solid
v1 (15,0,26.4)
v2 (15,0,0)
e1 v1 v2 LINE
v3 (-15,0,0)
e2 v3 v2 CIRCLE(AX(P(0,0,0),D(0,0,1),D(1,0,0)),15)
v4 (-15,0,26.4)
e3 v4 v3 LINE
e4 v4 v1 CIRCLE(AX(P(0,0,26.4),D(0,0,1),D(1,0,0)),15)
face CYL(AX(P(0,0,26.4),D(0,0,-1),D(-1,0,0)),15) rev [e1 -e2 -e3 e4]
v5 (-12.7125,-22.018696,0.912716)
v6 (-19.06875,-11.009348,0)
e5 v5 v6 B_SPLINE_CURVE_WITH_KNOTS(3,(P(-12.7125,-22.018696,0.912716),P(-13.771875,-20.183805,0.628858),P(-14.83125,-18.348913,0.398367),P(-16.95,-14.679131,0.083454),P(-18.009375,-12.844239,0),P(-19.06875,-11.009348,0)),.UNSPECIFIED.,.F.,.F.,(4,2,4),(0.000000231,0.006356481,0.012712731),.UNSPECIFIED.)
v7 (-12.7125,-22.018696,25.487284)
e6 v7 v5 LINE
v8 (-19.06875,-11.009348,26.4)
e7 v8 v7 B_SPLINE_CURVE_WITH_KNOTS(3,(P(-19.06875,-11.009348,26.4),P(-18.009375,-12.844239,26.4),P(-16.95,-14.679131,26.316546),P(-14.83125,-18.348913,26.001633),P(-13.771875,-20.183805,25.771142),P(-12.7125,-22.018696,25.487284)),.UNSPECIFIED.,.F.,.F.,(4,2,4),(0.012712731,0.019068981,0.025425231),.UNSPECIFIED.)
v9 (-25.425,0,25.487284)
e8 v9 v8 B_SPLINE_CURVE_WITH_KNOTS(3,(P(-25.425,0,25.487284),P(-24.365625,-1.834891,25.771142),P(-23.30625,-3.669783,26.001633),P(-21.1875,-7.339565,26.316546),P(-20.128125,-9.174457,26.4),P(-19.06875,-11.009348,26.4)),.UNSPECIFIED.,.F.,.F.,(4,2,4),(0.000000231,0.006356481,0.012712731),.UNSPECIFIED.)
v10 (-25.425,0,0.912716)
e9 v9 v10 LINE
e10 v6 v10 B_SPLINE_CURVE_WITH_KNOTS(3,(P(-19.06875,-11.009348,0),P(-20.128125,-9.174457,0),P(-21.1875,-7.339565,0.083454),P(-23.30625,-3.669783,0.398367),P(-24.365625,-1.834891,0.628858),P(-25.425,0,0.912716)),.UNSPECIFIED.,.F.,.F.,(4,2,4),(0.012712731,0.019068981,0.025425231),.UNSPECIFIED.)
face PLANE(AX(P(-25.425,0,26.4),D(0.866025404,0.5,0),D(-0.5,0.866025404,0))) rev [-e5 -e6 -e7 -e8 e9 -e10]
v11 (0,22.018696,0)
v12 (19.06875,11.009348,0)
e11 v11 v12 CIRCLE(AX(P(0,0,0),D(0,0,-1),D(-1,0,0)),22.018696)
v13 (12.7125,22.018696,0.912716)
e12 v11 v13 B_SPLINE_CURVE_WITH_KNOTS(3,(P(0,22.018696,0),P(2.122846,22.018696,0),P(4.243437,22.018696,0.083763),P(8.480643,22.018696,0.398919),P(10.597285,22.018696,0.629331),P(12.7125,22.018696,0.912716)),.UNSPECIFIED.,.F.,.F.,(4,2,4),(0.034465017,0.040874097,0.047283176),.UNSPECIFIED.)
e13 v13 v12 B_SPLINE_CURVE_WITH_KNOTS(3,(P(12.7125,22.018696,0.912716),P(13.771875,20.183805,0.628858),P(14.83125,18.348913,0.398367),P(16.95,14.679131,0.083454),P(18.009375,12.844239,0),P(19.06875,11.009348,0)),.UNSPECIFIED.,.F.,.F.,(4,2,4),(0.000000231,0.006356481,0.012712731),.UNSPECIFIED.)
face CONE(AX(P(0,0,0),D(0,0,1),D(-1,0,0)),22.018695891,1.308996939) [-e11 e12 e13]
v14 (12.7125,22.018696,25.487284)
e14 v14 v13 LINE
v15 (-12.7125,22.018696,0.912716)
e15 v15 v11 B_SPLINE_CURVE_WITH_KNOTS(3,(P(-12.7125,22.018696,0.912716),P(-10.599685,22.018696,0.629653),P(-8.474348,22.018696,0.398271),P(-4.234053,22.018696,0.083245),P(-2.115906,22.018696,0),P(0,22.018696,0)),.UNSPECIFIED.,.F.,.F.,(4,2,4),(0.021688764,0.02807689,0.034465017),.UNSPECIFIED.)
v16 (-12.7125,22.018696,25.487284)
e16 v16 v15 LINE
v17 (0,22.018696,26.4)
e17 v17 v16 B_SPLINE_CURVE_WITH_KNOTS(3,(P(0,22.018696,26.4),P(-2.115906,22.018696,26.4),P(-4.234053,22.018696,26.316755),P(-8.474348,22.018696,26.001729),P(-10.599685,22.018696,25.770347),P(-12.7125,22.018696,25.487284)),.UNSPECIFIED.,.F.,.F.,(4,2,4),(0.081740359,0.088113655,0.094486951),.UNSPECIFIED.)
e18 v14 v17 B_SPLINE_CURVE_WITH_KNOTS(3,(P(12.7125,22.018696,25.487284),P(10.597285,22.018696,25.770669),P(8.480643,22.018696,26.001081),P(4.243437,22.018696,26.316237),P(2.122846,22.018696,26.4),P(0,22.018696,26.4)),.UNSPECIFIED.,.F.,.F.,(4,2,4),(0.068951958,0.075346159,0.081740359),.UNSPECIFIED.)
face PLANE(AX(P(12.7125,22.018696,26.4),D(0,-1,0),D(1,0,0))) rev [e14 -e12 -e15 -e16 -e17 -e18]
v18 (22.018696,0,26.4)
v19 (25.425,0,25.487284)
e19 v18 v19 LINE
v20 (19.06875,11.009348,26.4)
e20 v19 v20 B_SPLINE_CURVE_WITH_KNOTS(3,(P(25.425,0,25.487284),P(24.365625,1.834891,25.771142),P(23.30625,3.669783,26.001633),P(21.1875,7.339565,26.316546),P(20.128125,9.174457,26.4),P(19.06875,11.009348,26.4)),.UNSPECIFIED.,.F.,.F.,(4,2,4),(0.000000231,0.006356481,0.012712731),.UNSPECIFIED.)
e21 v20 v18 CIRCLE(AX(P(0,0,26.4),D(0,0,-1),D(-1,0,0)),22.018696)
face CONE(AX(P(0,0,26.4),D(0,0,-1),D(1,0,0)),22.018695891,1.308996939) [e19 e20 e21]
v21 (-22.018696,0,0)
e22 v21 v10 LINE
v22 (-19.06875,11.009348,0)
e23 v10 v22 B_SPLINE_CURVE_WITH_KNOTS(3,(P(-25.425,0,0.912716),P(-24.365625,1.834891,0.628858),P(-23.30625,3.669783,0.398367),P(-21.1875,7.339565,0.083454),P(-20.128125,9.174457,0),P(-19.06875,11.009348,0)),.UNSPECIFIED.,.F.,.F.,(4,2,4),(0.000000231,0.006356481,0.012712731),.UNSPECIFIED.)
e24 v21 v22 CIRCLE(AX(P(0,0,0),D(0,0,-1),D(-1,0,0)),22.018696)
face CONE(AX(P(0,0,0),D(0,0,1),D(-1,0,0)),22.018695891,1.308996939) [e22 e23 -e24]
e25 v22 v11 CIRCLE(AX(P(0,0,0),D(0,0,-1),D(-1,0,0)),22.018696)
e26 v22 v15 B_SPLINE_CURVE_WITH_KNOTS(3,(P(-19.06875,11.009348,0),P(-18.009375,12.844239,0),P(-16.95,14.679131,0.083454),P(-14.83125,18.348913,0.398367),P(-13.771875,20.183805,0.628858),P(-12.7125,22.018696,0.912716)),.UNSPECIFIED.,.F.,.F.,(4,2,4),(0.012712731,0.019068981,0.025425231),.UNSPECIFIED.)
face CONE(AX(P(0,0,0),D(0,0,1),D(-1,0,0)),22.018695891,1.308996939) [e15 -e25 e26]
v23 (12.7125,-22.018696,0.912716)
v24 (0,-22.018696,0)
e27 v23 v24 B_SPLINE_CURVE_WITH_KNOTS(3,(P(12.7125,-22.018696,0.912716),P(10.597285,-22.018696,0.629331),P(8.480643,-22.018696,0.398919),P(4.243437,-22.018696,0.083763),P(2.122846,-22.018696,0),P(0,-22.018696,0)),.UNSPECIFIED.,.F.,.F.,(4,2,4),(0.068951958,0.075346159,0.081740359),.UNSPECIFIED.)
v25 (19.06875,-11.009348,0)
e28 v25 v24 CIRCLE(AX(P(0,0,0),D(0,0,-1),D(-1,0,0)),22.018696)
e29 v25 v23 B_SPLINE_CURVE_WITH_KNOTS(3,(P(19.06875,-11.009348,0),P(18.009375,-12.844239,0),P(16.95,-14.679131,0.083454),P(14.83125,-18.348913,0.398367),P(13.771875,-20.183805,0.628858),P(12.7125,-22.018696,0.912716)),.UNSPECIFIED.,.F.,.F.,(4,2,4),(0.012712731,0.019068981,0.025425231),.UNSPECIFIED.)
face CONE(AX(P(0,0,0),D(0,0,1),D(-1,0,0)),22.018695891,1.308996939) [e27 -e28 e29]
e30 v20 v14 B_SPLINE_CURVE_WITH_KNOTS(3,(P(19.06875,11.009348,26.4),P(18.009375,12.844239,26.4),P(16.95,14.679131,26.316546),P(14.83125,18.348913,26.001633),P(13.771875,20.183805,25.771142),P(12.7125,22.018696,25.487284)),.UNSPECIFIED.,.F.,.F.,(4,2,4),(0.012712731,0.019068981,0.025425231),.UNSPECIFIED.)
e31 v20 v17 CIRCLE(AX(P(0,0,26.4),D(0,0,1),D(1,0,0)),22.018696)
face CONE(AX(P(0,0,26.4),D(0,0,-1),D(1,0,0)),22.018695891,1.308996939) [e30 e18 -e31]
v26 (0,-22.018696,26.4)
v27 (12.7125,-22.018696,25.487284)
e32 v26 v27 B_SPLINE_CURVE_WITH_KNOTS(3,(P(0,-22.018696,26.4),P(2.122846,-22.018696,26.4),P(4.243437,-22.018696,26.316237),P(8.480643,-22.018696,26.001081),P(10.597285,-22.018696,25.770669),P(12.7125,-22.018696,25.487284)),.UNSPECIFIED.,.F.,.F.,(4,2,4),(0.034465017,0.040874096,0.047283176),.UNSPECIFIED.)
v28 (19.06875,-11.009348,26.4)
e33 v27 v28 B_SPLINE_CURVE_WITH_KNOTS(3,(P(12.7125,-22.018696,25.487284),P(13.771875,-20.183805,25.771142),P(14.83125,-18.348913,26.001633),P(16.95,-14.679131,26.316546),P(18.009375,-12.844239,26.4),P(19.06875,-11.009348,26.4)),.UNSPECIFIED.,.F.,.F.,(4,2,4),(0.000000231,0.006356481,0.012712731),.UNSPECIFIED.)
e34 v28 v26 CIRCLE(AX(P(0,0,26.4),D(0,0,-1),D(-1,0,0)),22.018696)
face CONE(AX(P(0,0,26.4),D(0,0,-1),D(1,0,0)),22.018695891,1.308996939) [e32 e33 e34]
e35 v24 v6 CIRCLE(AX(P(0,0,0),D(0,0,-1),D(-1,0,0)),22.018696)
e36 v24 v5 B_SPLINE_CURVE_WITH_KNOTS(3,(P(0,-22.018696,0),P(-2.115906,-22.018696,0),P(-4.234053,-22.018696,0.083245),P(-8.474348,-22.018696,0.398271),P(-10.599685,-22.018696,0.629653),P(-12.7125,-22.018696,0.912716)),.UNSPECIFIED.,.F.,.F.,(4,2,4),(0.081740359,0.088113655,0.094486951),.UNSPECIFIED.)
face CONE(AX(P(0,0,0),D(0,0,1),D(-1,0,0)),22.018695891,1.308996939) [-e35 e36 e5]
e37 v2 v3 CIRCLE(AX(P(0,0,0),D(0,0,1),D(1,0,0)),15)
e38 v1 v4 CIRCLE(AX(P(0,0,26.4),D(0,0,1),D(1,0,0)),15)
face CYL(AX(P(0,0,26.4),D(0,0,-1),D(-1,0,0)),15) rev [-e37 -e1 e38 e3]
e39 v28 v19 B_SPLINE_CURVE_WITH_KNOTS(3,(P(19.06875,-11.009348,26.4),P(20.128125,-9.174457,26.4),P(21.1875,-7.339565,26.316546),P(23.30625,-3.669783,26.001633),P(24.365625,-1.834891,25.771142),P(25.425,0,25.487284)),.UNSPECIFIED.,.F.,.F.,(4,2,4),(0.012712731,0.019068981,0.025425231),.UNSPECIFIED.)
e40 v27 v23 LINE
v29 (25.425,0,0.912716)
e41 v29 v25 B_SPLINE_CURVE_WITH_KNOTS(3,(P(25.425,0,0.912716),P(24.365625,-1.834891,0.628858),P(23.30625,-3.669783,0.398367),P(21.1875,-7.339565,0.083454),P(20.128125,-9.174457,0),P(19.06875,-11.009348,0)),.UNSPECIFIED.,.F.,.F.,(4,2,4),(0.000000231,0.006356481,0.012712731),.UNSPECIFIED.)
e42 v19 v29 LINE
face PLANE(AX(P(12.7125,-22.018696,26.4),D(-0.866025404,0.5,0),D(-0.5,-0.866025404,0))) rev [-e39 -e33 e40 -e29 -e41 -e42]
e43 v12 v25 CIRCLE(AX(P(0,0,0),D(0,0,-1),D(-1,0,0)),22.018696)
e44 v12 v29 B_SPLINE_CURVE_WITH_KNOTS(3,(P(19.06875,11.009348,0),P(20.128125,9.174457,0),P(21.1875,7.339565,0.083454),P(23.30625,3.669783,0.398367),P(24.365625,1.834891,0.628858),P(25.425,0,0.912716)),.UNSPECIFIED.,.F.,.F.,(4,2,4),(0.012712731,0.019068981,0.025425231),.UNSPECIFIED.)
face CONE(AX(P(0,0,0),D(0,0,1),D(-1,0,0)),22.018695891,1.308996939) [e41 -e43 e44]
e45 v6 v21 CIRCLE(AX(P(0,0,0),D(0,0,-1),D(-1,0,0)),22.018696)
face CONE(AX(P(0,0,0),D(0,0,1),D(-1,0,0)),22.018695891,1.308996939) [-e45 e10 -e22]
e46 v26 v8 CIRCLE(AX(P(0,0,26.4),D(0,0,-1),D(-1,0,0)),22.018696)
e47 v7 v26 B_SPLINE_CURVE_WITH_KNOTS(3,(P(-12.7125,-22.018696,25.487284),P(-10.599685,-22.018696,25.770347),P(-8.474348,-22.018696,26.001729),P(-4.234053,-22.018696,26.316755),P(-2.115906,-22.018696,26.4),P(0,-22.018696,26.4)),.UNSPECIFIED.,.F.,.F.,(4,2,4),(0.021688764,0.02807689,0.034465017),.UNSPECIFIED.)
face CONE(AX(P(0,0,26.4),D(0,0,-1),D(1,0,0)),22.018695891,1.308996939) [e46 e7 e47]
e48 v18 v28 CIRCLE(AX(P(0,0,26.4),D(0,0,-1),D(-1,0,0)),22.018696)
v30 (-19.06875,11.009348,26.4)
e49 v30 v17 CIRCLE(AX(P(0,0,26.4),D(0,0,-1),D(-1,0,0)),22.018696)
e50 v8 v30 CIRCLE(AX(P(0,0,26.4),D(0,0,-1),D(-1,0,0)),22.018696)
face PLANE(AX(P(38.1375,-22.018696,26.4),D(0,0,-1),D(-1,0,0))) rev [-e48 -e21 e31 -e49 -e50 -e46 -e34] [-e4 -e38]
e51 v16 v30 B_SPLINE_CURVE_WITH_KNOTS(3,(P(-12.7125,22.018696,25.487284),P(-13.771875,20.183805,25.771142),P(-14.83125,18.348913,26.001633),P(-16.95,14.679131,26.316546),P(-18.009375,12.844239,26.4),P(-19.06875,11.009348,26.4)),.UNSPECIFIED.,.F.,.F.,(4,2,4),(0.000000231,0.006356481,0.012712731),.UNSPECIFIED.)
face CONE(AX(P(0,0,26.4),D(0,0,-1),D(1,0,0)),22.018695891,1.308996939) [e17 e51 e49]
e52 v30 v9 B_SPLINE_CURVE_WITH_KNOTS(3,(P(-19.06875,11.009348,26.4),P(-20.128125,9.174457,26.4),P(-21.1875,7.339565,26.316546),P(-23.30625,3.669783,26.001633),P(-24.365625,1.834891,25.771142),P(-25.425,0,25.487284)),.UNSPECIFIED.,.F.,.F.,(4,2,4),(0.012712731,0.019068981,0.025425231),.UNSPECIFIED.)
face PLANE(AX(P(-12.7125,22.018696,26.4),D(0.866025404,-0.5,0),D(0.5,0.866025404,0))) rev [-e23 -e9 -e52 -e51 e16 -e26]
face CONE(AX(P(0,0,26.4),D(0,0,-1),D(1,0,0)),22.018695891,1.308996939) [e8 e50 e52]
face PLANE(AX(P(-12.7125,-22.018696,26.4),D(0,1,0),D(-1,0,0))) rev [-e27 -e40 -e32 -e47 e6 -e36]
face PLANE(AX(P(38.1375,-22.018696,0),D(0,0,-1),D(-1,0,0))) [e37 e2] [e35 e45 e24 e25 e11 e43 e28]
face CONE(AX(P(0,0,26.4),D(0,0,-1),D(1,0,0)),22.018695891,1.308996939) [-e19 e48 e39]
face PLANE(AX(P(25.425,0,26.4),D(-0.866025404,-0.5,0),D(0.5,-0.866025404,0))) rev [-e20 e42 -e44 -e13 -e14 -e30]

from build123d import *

# Parameters (mm, degrees)
SKETCH_1_R          = 15
EXTRUDE_519_DEPTH   = 26.4
SKETCH_2_OUTSIDE_W  = 350.938
SKETCH_2_OUTSIDE_H  = 344.126
SKETCH_2_OUTSIDE_R  = 22.018695891
CUT_EXTRUDE_1_DEPTH = 38
CUT_EXTRUDE_1_DRAFT = -75
SKETCH_3_OUTSIDE_W  = 350.938
SKETCH_3_OUTSIDE_H  = 344.126
SKETCH_3_OUTSIDE_R  = 22.018695891
CUT_EXTRUDE_2_DEPTH = 38
CUT_EXTRUDE_2_DRAFT = -75


with BuildPart() as part:
    # 草图1 → Extrude 519 (new body)
    with BuildSketch(Plane.XY):
        Polygon((12.7125, 22.018695891), (-12.7125, 22.018695891), (-25.425, 0), (-12.7125, -22.018695891), (12.7125, -22.018695891), (25.425, 0), align=None)
        Circle(SKETCH_1_R, mode=Mode.SUBTRACT)
    extrude(amount=EXTRUDE_519_DEPTH)


with BuildPart() as cut_extrude_1_tool:
    # 草图2 outside → 切除-拉伸1 (with draft: the straight prism first)
    with BuildSketch(Plane(origin=(0, 0, 0), x_dir=(-1, 0, 0), z_dir=(0, 0, -1))):
        Rectangle(SKETCH_2_OUTSIDE_W, SKETCH_2_OUTSIDE_H)
        Circle(SKETCH_2_OUTSIDE_R, mode=Mode.SUBTRACT)
    extrude(amount=-CUT_EXTRUDE_1_DEPTH)
    # 切除-拉伸1: the draft: its side faces are tilted about the plane it starts from
    cut_extrude_1_sides = [cut_extrude_1_tool.faces().sort_by_distance(p)[0] for p in [
        (0, -172.063, 19),
        (-175.469, 0, 19),
        (0, 172.063, 19),
        (175.469, 0, 19),
        (22.018695891, 0, 19),
    ]]
    draft(cut_extrude_1_sides, Plane(origin=(0, 0, 0), x_dir=(-1, 0, 0), z_dir=(0, 0, -1)), CUT_EXTRUDE_1_DRAFT)


with BuildPart() as part_1:
    add(part.part)

    # 切除-拉伸1: cut by cut_extrude_1_tool
    add(cut_extrude_1_tool.part, mode=Mode.SUBTRACT)


with BuildPart() as cut_extrude_2_tool:
    # 草图3 outside → 切除-拉伸2 (with draft: the straight prism first)
    with BuildSketch(Plane.XY.offset(26.4)):
        Rectangle(SKETCH_3_OUTSIDE_W, SKETCH_3_OUTSIDE_H)
        Circle(SKETCH_3_OUTSIDE_R, mode=Mode.SUBTRACT)
    extrude(amount=-CUT_EXTRUDE_2_DEPTH)
    # 切除-拉伸2: the draft: its side faces are tilted about the plane it starts from
    cut_extrude_2_sides = [cut_extrude_2_tool.faces().sort_by_distance(p)[0] for p in [
        (0, -172.063, 7.4),
        (175.469, 0, 7.4),
        (0, 172.063, 7.4),
        (-175.469, 0, 7.4),
        (-22.018695891, 0, 7.4),
    ]]
    draft(cut_extrude_2_sides, Plane.XY.offset(26.4), CUT_EXTRUDE_2_DRAFT)


with BuildPart() as part_2:
    add(part_1.part)

    # 切除-拉伸2: cut by cut_extrude_2_tool
    add(cut_extrude_2_tool.part, mode=Mode.SUBTRACT)


solid = part_2.part
